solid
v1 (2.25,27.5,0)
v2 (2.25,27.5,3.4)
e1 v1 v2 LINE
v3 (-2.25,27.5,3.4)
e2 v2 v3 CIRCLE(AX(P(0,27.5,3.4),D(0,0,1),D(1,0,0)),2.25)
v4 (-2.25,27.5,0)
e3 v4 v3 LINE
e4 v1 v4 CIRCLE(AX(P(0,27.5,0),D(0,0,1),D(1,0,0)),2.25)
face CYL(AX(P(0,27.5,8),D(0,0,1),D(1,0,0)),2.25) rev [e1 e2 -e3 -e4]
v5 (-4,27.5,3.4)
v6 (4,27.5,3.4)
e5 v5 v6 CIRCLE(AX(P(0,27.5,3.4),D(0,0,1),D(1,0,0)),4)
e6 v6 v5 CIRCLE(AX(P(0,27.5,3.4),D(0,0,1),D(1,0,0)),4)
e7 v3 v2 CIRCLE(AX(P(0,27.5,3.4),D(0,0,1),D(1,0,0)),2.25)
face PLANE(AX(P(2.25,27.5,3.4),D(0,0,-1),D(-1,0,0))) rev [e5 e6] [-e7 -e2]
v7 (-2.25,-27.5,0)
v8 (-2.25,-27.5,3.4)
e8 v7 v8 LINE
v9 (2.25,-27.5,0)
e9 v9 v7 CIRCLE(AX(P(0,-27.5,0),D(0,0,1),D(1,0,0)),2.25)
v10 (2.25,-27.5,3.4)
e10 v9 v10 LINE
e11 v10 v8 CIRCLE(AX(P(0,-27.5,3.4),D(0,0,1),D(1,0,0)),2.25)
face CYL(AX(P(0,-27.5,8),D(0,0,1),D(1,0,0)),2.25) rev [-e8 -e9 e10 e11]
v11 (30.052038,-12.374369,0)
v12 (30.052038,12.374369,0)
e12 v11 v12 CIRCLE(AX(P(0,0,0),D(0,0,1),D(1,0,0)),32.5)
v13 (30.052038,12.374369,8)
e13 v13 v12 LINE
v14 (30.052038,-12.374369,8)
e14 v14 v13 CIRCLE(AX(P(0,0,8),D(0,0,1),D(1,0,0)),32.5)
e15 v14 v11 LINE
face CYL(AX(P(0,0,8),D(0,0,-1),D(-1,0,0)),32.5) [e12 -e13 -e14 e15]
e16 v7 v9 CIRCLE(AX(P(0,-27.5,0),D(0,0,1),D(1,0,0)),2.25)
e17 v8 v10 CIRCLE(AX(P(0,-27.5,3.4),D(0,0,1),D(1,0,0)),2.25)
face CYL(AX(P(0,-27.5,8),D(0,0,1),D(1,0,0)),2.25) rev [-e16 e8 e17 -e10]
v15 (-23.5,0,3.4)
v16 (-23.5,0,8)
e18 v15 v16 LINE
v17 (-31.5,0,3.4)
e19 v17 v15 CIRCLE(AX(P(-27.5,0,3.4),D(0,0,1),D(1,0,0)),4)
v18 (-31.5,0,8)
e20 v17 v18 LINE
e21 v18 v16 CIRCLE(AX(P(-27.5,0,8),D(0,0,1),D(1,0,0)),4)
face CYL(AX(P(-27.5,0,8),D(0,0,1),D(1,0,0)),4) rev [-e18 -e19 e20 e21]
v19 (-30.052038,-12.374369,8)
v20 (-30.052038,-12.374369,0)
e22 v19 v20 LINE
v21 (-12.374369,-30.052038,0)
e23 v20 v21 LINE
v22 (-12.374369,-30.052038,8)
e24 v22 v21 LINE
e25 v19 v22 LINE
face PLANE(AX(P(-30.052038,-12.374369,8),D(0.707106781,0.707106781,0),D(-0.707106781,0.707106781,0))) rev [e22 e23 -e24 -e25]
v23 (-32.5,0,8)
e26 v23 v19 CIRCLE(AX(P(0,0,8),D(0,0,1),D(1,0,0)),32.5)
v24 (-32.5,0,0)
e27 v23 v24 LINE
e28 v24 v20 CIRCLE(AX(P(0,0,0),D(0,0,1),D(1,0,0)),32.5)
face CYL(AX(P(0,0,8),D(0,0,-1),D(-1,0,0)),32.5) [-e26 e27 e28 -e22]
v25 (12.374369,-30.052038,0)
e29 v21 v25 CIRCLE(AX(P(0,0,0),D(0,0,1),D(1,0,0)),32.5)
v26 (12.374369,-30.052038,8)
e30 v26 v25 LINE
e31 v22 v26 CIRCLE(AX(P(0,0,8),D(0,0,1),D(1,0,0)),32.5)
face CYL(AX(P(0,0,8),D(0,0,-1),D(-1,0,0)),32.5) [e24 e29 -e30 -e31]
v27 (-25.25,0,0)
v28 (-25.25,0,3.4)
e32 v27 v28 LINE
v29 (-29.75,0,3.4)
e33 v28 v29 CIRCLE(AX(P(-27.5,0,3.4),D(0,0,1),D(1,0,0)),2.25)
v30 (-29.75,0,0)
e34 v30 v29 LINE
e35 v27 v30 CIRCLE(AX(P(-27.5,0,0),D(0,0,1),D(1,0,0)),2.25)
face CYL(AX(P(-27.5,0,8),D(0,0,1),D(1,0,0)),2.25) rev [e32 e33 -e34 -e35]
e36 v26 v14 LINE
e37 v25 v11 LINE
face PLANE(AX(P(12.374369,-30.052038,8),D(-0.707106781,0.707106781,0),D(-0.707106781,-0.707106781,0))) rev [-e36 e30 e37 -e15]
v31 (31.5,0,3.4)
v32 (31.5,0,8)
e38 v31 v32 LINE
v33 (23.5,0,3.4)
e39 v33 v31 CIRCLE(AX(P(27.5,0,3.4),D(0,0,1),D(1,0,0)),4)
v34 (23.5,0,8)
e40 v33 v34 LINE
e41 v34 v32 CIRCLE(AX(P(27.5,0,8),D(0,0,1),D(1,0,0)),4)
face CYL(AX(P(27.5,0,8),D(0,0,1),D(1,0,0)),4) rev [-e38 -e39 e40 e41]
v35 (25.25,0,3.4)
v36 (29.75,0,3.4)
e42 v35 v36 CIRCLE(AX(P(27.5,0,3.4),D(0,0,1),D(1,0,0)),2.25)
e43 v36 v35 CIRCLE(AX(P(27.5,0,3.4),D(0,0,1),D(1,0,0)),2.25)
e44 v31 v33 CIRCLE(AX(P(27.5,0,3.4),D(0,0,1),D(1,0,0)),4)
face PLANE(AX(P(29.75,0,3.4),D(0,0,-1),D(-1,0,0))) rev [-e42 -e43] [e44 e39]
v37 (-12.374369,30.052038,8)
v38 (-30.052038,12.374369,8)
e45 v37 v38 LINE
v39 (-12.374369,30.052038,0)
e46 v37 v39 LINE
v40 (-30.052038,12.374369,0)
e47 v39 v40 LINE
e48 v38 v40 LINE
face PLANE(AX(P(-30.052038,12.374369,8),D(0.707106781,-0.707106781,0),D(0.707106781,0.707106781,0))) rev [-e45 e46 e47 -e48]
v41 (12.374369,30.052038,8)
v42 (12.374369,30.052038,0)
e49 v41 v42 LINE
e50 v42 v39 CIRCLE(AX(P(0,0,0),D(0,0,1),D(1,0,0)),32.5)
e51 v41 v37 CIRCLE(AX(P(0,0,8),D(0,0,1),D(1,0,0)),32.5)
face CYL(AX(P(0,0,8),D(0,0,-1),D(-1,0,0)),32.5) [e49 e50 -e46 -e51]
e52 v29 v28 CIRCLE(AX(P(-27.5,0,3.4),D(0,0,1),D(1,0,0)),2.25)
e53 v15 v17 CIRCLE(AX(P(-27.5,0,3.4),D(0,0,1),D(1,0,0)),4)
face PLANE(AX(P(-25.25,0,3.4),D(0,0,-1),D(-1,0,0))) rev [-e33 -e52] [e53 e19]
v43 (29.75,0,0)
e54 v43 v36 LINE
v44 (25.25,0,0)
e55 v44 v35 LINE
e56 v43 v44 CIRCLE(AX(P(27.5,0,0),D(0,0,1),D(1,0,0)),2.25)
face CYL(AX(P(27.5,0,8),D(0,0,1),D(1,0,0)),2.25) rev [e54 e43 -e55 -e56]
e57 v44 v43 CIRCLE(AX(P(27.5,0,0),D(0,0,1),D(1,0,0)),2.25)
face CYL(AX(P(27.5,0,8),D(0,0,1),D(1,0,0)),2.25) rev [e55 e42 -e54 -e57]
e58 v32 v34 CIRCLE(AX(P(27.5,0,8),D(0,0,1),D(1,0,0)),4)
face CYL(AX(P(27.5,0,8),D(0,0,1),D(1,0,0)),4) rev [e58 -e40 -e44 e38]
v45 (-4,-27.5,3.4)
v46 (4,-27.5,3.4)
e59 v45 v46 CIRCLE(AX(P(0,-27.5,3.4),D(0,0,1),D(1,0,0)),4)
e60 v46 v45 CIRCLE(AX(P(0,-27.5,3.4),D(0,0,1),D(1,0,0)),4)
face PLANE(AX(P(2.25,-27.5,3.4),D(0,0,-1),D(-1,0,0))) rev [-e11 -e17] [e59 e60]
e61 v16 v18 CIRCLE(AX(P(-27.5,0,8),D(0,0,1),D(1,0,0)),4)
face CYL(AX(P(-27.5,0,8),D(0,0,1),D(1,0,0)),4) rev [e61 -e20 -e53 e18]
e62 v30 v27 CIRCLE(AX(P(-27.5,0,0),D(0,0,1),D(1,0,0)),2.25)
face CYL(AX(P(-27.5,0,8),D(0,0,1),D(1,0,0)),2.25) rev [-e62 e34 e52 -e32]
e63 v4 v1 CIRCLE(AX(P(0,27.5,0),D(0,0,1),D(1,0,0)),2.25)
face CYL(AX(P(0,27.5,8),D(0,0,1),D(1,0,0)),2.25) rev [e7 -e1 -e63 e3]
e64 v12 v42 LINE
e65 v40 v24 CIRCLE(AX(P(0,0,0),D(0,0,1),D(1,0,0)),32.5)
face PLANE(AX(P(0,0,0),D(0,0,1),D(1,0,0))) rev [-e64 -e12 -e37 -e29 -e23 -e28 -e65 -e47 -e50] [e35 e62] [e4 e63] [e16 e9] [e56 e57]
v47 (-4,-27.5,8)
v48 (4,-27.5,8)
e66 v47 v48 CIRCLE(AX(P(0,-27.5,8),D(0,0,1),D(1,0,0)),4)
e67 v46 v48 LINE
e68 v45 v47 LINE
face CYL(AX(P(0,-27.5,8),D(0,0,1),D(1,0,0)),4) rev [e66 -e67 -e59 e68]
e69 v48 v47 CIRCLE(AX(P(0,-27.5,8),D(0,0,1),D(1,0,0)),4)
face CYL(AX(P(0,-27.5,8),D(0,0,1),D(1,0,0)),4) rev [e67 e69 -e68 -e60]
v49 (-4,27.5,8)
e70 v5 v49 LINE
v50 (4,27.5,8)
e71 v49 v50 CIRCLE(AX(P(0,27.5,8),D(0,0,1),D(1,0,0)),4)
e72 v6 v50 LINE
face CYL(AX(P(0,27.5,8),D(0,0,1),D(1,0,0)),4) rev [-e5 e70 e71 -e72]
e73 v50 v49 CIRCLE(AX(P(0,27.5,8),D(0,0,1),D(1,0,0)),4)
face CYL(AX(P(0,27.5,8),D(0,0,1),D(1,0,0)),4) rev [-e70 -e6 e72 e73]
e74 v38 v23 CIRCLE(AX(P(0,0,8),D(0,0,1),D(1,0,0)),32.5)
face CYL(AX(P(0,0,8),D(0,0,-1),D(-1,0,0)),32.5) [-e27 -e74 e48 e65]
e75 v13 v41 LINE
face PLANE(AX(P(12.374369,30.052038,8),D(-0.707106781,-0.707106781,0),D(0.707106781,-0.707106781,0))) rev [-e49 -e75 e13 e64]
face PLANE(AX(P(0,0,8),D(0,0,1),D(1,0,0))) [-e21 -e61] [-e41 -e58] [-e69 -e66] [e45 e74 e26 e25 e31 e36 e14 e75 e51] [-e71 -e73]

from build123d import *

# Parameters (mm, degrees)
BOSS_EXTRUDE1_DEPTH                                  = 8
HOLE_SIZE_PER_SOCKET_HEAD_CAP_SCREW_TYPE_D           = 4.5
HOLE_SIZE_PER_SOCKET_HEAD_CAP_SCREW_TYPE_CBORE_D     = 8
HOLE_SIZE_PER_SOCKET_HEAD_CAP_SCREW_TYPE_CBORE_DEPTH = 4.6


with BuildPart() as part:
    # Sketch1 → Boss-Extrude1 (new body)
    with BuildSketch(Plane.XY):
        with BuildLine():
            Line((-30.0520382, -12.374368671), (-12.374368671, -30.0520382))
            ThreePointArc((-12.374368671, -30.0520382), (0, -32.5), (12.374368671, -30.0520382))
            Line((12.374368671, -30.0520382), (30.0520382, -12.374368671))
            ThreePointArc((30.0520382, -12.374368671), (32.5, 0), (30.0520382, 12.374368671))
            Line((30.0520382, 12.374368671), (12.374368671, 30.0520382))
            ThreePointArc((12.374368671, 30.0520382), (0, 32.5), (-12.374368671, 30.0520382))
            Line((-12.374368671, 30.0520382), (-30.0520382, 12.374368671))
            ThreePointArc((-30.0520382, 12.374368671), (-32.5, 0), (-30.0520382, -12.374368671))
        make_face()
    extrude(amount=BOSS_EXTRUDE1_DEPTH)

    # Hole size per socket head cap screw type 1 (through all)
    with Locations(Plane.XY.offset(8)):
        with Locations((0, 27.5), (-27.5, 0), (0, -27.5), (27.5, 0)):
            CounterBoreHole(HOLE_SIZE_PER_SOCKET_HEAD_CAP_SCREW_TYPE_D / 2, HOLE_SIZE_PER_SOCKET_HEAD_CAP_SCREW_TYPE_CBORE_D / 2, HOLE_SIZE_PER_SOCKET_HEAD_CAP_SCREW_TYPE_CBORE_DEPTH)


solid = part.part
